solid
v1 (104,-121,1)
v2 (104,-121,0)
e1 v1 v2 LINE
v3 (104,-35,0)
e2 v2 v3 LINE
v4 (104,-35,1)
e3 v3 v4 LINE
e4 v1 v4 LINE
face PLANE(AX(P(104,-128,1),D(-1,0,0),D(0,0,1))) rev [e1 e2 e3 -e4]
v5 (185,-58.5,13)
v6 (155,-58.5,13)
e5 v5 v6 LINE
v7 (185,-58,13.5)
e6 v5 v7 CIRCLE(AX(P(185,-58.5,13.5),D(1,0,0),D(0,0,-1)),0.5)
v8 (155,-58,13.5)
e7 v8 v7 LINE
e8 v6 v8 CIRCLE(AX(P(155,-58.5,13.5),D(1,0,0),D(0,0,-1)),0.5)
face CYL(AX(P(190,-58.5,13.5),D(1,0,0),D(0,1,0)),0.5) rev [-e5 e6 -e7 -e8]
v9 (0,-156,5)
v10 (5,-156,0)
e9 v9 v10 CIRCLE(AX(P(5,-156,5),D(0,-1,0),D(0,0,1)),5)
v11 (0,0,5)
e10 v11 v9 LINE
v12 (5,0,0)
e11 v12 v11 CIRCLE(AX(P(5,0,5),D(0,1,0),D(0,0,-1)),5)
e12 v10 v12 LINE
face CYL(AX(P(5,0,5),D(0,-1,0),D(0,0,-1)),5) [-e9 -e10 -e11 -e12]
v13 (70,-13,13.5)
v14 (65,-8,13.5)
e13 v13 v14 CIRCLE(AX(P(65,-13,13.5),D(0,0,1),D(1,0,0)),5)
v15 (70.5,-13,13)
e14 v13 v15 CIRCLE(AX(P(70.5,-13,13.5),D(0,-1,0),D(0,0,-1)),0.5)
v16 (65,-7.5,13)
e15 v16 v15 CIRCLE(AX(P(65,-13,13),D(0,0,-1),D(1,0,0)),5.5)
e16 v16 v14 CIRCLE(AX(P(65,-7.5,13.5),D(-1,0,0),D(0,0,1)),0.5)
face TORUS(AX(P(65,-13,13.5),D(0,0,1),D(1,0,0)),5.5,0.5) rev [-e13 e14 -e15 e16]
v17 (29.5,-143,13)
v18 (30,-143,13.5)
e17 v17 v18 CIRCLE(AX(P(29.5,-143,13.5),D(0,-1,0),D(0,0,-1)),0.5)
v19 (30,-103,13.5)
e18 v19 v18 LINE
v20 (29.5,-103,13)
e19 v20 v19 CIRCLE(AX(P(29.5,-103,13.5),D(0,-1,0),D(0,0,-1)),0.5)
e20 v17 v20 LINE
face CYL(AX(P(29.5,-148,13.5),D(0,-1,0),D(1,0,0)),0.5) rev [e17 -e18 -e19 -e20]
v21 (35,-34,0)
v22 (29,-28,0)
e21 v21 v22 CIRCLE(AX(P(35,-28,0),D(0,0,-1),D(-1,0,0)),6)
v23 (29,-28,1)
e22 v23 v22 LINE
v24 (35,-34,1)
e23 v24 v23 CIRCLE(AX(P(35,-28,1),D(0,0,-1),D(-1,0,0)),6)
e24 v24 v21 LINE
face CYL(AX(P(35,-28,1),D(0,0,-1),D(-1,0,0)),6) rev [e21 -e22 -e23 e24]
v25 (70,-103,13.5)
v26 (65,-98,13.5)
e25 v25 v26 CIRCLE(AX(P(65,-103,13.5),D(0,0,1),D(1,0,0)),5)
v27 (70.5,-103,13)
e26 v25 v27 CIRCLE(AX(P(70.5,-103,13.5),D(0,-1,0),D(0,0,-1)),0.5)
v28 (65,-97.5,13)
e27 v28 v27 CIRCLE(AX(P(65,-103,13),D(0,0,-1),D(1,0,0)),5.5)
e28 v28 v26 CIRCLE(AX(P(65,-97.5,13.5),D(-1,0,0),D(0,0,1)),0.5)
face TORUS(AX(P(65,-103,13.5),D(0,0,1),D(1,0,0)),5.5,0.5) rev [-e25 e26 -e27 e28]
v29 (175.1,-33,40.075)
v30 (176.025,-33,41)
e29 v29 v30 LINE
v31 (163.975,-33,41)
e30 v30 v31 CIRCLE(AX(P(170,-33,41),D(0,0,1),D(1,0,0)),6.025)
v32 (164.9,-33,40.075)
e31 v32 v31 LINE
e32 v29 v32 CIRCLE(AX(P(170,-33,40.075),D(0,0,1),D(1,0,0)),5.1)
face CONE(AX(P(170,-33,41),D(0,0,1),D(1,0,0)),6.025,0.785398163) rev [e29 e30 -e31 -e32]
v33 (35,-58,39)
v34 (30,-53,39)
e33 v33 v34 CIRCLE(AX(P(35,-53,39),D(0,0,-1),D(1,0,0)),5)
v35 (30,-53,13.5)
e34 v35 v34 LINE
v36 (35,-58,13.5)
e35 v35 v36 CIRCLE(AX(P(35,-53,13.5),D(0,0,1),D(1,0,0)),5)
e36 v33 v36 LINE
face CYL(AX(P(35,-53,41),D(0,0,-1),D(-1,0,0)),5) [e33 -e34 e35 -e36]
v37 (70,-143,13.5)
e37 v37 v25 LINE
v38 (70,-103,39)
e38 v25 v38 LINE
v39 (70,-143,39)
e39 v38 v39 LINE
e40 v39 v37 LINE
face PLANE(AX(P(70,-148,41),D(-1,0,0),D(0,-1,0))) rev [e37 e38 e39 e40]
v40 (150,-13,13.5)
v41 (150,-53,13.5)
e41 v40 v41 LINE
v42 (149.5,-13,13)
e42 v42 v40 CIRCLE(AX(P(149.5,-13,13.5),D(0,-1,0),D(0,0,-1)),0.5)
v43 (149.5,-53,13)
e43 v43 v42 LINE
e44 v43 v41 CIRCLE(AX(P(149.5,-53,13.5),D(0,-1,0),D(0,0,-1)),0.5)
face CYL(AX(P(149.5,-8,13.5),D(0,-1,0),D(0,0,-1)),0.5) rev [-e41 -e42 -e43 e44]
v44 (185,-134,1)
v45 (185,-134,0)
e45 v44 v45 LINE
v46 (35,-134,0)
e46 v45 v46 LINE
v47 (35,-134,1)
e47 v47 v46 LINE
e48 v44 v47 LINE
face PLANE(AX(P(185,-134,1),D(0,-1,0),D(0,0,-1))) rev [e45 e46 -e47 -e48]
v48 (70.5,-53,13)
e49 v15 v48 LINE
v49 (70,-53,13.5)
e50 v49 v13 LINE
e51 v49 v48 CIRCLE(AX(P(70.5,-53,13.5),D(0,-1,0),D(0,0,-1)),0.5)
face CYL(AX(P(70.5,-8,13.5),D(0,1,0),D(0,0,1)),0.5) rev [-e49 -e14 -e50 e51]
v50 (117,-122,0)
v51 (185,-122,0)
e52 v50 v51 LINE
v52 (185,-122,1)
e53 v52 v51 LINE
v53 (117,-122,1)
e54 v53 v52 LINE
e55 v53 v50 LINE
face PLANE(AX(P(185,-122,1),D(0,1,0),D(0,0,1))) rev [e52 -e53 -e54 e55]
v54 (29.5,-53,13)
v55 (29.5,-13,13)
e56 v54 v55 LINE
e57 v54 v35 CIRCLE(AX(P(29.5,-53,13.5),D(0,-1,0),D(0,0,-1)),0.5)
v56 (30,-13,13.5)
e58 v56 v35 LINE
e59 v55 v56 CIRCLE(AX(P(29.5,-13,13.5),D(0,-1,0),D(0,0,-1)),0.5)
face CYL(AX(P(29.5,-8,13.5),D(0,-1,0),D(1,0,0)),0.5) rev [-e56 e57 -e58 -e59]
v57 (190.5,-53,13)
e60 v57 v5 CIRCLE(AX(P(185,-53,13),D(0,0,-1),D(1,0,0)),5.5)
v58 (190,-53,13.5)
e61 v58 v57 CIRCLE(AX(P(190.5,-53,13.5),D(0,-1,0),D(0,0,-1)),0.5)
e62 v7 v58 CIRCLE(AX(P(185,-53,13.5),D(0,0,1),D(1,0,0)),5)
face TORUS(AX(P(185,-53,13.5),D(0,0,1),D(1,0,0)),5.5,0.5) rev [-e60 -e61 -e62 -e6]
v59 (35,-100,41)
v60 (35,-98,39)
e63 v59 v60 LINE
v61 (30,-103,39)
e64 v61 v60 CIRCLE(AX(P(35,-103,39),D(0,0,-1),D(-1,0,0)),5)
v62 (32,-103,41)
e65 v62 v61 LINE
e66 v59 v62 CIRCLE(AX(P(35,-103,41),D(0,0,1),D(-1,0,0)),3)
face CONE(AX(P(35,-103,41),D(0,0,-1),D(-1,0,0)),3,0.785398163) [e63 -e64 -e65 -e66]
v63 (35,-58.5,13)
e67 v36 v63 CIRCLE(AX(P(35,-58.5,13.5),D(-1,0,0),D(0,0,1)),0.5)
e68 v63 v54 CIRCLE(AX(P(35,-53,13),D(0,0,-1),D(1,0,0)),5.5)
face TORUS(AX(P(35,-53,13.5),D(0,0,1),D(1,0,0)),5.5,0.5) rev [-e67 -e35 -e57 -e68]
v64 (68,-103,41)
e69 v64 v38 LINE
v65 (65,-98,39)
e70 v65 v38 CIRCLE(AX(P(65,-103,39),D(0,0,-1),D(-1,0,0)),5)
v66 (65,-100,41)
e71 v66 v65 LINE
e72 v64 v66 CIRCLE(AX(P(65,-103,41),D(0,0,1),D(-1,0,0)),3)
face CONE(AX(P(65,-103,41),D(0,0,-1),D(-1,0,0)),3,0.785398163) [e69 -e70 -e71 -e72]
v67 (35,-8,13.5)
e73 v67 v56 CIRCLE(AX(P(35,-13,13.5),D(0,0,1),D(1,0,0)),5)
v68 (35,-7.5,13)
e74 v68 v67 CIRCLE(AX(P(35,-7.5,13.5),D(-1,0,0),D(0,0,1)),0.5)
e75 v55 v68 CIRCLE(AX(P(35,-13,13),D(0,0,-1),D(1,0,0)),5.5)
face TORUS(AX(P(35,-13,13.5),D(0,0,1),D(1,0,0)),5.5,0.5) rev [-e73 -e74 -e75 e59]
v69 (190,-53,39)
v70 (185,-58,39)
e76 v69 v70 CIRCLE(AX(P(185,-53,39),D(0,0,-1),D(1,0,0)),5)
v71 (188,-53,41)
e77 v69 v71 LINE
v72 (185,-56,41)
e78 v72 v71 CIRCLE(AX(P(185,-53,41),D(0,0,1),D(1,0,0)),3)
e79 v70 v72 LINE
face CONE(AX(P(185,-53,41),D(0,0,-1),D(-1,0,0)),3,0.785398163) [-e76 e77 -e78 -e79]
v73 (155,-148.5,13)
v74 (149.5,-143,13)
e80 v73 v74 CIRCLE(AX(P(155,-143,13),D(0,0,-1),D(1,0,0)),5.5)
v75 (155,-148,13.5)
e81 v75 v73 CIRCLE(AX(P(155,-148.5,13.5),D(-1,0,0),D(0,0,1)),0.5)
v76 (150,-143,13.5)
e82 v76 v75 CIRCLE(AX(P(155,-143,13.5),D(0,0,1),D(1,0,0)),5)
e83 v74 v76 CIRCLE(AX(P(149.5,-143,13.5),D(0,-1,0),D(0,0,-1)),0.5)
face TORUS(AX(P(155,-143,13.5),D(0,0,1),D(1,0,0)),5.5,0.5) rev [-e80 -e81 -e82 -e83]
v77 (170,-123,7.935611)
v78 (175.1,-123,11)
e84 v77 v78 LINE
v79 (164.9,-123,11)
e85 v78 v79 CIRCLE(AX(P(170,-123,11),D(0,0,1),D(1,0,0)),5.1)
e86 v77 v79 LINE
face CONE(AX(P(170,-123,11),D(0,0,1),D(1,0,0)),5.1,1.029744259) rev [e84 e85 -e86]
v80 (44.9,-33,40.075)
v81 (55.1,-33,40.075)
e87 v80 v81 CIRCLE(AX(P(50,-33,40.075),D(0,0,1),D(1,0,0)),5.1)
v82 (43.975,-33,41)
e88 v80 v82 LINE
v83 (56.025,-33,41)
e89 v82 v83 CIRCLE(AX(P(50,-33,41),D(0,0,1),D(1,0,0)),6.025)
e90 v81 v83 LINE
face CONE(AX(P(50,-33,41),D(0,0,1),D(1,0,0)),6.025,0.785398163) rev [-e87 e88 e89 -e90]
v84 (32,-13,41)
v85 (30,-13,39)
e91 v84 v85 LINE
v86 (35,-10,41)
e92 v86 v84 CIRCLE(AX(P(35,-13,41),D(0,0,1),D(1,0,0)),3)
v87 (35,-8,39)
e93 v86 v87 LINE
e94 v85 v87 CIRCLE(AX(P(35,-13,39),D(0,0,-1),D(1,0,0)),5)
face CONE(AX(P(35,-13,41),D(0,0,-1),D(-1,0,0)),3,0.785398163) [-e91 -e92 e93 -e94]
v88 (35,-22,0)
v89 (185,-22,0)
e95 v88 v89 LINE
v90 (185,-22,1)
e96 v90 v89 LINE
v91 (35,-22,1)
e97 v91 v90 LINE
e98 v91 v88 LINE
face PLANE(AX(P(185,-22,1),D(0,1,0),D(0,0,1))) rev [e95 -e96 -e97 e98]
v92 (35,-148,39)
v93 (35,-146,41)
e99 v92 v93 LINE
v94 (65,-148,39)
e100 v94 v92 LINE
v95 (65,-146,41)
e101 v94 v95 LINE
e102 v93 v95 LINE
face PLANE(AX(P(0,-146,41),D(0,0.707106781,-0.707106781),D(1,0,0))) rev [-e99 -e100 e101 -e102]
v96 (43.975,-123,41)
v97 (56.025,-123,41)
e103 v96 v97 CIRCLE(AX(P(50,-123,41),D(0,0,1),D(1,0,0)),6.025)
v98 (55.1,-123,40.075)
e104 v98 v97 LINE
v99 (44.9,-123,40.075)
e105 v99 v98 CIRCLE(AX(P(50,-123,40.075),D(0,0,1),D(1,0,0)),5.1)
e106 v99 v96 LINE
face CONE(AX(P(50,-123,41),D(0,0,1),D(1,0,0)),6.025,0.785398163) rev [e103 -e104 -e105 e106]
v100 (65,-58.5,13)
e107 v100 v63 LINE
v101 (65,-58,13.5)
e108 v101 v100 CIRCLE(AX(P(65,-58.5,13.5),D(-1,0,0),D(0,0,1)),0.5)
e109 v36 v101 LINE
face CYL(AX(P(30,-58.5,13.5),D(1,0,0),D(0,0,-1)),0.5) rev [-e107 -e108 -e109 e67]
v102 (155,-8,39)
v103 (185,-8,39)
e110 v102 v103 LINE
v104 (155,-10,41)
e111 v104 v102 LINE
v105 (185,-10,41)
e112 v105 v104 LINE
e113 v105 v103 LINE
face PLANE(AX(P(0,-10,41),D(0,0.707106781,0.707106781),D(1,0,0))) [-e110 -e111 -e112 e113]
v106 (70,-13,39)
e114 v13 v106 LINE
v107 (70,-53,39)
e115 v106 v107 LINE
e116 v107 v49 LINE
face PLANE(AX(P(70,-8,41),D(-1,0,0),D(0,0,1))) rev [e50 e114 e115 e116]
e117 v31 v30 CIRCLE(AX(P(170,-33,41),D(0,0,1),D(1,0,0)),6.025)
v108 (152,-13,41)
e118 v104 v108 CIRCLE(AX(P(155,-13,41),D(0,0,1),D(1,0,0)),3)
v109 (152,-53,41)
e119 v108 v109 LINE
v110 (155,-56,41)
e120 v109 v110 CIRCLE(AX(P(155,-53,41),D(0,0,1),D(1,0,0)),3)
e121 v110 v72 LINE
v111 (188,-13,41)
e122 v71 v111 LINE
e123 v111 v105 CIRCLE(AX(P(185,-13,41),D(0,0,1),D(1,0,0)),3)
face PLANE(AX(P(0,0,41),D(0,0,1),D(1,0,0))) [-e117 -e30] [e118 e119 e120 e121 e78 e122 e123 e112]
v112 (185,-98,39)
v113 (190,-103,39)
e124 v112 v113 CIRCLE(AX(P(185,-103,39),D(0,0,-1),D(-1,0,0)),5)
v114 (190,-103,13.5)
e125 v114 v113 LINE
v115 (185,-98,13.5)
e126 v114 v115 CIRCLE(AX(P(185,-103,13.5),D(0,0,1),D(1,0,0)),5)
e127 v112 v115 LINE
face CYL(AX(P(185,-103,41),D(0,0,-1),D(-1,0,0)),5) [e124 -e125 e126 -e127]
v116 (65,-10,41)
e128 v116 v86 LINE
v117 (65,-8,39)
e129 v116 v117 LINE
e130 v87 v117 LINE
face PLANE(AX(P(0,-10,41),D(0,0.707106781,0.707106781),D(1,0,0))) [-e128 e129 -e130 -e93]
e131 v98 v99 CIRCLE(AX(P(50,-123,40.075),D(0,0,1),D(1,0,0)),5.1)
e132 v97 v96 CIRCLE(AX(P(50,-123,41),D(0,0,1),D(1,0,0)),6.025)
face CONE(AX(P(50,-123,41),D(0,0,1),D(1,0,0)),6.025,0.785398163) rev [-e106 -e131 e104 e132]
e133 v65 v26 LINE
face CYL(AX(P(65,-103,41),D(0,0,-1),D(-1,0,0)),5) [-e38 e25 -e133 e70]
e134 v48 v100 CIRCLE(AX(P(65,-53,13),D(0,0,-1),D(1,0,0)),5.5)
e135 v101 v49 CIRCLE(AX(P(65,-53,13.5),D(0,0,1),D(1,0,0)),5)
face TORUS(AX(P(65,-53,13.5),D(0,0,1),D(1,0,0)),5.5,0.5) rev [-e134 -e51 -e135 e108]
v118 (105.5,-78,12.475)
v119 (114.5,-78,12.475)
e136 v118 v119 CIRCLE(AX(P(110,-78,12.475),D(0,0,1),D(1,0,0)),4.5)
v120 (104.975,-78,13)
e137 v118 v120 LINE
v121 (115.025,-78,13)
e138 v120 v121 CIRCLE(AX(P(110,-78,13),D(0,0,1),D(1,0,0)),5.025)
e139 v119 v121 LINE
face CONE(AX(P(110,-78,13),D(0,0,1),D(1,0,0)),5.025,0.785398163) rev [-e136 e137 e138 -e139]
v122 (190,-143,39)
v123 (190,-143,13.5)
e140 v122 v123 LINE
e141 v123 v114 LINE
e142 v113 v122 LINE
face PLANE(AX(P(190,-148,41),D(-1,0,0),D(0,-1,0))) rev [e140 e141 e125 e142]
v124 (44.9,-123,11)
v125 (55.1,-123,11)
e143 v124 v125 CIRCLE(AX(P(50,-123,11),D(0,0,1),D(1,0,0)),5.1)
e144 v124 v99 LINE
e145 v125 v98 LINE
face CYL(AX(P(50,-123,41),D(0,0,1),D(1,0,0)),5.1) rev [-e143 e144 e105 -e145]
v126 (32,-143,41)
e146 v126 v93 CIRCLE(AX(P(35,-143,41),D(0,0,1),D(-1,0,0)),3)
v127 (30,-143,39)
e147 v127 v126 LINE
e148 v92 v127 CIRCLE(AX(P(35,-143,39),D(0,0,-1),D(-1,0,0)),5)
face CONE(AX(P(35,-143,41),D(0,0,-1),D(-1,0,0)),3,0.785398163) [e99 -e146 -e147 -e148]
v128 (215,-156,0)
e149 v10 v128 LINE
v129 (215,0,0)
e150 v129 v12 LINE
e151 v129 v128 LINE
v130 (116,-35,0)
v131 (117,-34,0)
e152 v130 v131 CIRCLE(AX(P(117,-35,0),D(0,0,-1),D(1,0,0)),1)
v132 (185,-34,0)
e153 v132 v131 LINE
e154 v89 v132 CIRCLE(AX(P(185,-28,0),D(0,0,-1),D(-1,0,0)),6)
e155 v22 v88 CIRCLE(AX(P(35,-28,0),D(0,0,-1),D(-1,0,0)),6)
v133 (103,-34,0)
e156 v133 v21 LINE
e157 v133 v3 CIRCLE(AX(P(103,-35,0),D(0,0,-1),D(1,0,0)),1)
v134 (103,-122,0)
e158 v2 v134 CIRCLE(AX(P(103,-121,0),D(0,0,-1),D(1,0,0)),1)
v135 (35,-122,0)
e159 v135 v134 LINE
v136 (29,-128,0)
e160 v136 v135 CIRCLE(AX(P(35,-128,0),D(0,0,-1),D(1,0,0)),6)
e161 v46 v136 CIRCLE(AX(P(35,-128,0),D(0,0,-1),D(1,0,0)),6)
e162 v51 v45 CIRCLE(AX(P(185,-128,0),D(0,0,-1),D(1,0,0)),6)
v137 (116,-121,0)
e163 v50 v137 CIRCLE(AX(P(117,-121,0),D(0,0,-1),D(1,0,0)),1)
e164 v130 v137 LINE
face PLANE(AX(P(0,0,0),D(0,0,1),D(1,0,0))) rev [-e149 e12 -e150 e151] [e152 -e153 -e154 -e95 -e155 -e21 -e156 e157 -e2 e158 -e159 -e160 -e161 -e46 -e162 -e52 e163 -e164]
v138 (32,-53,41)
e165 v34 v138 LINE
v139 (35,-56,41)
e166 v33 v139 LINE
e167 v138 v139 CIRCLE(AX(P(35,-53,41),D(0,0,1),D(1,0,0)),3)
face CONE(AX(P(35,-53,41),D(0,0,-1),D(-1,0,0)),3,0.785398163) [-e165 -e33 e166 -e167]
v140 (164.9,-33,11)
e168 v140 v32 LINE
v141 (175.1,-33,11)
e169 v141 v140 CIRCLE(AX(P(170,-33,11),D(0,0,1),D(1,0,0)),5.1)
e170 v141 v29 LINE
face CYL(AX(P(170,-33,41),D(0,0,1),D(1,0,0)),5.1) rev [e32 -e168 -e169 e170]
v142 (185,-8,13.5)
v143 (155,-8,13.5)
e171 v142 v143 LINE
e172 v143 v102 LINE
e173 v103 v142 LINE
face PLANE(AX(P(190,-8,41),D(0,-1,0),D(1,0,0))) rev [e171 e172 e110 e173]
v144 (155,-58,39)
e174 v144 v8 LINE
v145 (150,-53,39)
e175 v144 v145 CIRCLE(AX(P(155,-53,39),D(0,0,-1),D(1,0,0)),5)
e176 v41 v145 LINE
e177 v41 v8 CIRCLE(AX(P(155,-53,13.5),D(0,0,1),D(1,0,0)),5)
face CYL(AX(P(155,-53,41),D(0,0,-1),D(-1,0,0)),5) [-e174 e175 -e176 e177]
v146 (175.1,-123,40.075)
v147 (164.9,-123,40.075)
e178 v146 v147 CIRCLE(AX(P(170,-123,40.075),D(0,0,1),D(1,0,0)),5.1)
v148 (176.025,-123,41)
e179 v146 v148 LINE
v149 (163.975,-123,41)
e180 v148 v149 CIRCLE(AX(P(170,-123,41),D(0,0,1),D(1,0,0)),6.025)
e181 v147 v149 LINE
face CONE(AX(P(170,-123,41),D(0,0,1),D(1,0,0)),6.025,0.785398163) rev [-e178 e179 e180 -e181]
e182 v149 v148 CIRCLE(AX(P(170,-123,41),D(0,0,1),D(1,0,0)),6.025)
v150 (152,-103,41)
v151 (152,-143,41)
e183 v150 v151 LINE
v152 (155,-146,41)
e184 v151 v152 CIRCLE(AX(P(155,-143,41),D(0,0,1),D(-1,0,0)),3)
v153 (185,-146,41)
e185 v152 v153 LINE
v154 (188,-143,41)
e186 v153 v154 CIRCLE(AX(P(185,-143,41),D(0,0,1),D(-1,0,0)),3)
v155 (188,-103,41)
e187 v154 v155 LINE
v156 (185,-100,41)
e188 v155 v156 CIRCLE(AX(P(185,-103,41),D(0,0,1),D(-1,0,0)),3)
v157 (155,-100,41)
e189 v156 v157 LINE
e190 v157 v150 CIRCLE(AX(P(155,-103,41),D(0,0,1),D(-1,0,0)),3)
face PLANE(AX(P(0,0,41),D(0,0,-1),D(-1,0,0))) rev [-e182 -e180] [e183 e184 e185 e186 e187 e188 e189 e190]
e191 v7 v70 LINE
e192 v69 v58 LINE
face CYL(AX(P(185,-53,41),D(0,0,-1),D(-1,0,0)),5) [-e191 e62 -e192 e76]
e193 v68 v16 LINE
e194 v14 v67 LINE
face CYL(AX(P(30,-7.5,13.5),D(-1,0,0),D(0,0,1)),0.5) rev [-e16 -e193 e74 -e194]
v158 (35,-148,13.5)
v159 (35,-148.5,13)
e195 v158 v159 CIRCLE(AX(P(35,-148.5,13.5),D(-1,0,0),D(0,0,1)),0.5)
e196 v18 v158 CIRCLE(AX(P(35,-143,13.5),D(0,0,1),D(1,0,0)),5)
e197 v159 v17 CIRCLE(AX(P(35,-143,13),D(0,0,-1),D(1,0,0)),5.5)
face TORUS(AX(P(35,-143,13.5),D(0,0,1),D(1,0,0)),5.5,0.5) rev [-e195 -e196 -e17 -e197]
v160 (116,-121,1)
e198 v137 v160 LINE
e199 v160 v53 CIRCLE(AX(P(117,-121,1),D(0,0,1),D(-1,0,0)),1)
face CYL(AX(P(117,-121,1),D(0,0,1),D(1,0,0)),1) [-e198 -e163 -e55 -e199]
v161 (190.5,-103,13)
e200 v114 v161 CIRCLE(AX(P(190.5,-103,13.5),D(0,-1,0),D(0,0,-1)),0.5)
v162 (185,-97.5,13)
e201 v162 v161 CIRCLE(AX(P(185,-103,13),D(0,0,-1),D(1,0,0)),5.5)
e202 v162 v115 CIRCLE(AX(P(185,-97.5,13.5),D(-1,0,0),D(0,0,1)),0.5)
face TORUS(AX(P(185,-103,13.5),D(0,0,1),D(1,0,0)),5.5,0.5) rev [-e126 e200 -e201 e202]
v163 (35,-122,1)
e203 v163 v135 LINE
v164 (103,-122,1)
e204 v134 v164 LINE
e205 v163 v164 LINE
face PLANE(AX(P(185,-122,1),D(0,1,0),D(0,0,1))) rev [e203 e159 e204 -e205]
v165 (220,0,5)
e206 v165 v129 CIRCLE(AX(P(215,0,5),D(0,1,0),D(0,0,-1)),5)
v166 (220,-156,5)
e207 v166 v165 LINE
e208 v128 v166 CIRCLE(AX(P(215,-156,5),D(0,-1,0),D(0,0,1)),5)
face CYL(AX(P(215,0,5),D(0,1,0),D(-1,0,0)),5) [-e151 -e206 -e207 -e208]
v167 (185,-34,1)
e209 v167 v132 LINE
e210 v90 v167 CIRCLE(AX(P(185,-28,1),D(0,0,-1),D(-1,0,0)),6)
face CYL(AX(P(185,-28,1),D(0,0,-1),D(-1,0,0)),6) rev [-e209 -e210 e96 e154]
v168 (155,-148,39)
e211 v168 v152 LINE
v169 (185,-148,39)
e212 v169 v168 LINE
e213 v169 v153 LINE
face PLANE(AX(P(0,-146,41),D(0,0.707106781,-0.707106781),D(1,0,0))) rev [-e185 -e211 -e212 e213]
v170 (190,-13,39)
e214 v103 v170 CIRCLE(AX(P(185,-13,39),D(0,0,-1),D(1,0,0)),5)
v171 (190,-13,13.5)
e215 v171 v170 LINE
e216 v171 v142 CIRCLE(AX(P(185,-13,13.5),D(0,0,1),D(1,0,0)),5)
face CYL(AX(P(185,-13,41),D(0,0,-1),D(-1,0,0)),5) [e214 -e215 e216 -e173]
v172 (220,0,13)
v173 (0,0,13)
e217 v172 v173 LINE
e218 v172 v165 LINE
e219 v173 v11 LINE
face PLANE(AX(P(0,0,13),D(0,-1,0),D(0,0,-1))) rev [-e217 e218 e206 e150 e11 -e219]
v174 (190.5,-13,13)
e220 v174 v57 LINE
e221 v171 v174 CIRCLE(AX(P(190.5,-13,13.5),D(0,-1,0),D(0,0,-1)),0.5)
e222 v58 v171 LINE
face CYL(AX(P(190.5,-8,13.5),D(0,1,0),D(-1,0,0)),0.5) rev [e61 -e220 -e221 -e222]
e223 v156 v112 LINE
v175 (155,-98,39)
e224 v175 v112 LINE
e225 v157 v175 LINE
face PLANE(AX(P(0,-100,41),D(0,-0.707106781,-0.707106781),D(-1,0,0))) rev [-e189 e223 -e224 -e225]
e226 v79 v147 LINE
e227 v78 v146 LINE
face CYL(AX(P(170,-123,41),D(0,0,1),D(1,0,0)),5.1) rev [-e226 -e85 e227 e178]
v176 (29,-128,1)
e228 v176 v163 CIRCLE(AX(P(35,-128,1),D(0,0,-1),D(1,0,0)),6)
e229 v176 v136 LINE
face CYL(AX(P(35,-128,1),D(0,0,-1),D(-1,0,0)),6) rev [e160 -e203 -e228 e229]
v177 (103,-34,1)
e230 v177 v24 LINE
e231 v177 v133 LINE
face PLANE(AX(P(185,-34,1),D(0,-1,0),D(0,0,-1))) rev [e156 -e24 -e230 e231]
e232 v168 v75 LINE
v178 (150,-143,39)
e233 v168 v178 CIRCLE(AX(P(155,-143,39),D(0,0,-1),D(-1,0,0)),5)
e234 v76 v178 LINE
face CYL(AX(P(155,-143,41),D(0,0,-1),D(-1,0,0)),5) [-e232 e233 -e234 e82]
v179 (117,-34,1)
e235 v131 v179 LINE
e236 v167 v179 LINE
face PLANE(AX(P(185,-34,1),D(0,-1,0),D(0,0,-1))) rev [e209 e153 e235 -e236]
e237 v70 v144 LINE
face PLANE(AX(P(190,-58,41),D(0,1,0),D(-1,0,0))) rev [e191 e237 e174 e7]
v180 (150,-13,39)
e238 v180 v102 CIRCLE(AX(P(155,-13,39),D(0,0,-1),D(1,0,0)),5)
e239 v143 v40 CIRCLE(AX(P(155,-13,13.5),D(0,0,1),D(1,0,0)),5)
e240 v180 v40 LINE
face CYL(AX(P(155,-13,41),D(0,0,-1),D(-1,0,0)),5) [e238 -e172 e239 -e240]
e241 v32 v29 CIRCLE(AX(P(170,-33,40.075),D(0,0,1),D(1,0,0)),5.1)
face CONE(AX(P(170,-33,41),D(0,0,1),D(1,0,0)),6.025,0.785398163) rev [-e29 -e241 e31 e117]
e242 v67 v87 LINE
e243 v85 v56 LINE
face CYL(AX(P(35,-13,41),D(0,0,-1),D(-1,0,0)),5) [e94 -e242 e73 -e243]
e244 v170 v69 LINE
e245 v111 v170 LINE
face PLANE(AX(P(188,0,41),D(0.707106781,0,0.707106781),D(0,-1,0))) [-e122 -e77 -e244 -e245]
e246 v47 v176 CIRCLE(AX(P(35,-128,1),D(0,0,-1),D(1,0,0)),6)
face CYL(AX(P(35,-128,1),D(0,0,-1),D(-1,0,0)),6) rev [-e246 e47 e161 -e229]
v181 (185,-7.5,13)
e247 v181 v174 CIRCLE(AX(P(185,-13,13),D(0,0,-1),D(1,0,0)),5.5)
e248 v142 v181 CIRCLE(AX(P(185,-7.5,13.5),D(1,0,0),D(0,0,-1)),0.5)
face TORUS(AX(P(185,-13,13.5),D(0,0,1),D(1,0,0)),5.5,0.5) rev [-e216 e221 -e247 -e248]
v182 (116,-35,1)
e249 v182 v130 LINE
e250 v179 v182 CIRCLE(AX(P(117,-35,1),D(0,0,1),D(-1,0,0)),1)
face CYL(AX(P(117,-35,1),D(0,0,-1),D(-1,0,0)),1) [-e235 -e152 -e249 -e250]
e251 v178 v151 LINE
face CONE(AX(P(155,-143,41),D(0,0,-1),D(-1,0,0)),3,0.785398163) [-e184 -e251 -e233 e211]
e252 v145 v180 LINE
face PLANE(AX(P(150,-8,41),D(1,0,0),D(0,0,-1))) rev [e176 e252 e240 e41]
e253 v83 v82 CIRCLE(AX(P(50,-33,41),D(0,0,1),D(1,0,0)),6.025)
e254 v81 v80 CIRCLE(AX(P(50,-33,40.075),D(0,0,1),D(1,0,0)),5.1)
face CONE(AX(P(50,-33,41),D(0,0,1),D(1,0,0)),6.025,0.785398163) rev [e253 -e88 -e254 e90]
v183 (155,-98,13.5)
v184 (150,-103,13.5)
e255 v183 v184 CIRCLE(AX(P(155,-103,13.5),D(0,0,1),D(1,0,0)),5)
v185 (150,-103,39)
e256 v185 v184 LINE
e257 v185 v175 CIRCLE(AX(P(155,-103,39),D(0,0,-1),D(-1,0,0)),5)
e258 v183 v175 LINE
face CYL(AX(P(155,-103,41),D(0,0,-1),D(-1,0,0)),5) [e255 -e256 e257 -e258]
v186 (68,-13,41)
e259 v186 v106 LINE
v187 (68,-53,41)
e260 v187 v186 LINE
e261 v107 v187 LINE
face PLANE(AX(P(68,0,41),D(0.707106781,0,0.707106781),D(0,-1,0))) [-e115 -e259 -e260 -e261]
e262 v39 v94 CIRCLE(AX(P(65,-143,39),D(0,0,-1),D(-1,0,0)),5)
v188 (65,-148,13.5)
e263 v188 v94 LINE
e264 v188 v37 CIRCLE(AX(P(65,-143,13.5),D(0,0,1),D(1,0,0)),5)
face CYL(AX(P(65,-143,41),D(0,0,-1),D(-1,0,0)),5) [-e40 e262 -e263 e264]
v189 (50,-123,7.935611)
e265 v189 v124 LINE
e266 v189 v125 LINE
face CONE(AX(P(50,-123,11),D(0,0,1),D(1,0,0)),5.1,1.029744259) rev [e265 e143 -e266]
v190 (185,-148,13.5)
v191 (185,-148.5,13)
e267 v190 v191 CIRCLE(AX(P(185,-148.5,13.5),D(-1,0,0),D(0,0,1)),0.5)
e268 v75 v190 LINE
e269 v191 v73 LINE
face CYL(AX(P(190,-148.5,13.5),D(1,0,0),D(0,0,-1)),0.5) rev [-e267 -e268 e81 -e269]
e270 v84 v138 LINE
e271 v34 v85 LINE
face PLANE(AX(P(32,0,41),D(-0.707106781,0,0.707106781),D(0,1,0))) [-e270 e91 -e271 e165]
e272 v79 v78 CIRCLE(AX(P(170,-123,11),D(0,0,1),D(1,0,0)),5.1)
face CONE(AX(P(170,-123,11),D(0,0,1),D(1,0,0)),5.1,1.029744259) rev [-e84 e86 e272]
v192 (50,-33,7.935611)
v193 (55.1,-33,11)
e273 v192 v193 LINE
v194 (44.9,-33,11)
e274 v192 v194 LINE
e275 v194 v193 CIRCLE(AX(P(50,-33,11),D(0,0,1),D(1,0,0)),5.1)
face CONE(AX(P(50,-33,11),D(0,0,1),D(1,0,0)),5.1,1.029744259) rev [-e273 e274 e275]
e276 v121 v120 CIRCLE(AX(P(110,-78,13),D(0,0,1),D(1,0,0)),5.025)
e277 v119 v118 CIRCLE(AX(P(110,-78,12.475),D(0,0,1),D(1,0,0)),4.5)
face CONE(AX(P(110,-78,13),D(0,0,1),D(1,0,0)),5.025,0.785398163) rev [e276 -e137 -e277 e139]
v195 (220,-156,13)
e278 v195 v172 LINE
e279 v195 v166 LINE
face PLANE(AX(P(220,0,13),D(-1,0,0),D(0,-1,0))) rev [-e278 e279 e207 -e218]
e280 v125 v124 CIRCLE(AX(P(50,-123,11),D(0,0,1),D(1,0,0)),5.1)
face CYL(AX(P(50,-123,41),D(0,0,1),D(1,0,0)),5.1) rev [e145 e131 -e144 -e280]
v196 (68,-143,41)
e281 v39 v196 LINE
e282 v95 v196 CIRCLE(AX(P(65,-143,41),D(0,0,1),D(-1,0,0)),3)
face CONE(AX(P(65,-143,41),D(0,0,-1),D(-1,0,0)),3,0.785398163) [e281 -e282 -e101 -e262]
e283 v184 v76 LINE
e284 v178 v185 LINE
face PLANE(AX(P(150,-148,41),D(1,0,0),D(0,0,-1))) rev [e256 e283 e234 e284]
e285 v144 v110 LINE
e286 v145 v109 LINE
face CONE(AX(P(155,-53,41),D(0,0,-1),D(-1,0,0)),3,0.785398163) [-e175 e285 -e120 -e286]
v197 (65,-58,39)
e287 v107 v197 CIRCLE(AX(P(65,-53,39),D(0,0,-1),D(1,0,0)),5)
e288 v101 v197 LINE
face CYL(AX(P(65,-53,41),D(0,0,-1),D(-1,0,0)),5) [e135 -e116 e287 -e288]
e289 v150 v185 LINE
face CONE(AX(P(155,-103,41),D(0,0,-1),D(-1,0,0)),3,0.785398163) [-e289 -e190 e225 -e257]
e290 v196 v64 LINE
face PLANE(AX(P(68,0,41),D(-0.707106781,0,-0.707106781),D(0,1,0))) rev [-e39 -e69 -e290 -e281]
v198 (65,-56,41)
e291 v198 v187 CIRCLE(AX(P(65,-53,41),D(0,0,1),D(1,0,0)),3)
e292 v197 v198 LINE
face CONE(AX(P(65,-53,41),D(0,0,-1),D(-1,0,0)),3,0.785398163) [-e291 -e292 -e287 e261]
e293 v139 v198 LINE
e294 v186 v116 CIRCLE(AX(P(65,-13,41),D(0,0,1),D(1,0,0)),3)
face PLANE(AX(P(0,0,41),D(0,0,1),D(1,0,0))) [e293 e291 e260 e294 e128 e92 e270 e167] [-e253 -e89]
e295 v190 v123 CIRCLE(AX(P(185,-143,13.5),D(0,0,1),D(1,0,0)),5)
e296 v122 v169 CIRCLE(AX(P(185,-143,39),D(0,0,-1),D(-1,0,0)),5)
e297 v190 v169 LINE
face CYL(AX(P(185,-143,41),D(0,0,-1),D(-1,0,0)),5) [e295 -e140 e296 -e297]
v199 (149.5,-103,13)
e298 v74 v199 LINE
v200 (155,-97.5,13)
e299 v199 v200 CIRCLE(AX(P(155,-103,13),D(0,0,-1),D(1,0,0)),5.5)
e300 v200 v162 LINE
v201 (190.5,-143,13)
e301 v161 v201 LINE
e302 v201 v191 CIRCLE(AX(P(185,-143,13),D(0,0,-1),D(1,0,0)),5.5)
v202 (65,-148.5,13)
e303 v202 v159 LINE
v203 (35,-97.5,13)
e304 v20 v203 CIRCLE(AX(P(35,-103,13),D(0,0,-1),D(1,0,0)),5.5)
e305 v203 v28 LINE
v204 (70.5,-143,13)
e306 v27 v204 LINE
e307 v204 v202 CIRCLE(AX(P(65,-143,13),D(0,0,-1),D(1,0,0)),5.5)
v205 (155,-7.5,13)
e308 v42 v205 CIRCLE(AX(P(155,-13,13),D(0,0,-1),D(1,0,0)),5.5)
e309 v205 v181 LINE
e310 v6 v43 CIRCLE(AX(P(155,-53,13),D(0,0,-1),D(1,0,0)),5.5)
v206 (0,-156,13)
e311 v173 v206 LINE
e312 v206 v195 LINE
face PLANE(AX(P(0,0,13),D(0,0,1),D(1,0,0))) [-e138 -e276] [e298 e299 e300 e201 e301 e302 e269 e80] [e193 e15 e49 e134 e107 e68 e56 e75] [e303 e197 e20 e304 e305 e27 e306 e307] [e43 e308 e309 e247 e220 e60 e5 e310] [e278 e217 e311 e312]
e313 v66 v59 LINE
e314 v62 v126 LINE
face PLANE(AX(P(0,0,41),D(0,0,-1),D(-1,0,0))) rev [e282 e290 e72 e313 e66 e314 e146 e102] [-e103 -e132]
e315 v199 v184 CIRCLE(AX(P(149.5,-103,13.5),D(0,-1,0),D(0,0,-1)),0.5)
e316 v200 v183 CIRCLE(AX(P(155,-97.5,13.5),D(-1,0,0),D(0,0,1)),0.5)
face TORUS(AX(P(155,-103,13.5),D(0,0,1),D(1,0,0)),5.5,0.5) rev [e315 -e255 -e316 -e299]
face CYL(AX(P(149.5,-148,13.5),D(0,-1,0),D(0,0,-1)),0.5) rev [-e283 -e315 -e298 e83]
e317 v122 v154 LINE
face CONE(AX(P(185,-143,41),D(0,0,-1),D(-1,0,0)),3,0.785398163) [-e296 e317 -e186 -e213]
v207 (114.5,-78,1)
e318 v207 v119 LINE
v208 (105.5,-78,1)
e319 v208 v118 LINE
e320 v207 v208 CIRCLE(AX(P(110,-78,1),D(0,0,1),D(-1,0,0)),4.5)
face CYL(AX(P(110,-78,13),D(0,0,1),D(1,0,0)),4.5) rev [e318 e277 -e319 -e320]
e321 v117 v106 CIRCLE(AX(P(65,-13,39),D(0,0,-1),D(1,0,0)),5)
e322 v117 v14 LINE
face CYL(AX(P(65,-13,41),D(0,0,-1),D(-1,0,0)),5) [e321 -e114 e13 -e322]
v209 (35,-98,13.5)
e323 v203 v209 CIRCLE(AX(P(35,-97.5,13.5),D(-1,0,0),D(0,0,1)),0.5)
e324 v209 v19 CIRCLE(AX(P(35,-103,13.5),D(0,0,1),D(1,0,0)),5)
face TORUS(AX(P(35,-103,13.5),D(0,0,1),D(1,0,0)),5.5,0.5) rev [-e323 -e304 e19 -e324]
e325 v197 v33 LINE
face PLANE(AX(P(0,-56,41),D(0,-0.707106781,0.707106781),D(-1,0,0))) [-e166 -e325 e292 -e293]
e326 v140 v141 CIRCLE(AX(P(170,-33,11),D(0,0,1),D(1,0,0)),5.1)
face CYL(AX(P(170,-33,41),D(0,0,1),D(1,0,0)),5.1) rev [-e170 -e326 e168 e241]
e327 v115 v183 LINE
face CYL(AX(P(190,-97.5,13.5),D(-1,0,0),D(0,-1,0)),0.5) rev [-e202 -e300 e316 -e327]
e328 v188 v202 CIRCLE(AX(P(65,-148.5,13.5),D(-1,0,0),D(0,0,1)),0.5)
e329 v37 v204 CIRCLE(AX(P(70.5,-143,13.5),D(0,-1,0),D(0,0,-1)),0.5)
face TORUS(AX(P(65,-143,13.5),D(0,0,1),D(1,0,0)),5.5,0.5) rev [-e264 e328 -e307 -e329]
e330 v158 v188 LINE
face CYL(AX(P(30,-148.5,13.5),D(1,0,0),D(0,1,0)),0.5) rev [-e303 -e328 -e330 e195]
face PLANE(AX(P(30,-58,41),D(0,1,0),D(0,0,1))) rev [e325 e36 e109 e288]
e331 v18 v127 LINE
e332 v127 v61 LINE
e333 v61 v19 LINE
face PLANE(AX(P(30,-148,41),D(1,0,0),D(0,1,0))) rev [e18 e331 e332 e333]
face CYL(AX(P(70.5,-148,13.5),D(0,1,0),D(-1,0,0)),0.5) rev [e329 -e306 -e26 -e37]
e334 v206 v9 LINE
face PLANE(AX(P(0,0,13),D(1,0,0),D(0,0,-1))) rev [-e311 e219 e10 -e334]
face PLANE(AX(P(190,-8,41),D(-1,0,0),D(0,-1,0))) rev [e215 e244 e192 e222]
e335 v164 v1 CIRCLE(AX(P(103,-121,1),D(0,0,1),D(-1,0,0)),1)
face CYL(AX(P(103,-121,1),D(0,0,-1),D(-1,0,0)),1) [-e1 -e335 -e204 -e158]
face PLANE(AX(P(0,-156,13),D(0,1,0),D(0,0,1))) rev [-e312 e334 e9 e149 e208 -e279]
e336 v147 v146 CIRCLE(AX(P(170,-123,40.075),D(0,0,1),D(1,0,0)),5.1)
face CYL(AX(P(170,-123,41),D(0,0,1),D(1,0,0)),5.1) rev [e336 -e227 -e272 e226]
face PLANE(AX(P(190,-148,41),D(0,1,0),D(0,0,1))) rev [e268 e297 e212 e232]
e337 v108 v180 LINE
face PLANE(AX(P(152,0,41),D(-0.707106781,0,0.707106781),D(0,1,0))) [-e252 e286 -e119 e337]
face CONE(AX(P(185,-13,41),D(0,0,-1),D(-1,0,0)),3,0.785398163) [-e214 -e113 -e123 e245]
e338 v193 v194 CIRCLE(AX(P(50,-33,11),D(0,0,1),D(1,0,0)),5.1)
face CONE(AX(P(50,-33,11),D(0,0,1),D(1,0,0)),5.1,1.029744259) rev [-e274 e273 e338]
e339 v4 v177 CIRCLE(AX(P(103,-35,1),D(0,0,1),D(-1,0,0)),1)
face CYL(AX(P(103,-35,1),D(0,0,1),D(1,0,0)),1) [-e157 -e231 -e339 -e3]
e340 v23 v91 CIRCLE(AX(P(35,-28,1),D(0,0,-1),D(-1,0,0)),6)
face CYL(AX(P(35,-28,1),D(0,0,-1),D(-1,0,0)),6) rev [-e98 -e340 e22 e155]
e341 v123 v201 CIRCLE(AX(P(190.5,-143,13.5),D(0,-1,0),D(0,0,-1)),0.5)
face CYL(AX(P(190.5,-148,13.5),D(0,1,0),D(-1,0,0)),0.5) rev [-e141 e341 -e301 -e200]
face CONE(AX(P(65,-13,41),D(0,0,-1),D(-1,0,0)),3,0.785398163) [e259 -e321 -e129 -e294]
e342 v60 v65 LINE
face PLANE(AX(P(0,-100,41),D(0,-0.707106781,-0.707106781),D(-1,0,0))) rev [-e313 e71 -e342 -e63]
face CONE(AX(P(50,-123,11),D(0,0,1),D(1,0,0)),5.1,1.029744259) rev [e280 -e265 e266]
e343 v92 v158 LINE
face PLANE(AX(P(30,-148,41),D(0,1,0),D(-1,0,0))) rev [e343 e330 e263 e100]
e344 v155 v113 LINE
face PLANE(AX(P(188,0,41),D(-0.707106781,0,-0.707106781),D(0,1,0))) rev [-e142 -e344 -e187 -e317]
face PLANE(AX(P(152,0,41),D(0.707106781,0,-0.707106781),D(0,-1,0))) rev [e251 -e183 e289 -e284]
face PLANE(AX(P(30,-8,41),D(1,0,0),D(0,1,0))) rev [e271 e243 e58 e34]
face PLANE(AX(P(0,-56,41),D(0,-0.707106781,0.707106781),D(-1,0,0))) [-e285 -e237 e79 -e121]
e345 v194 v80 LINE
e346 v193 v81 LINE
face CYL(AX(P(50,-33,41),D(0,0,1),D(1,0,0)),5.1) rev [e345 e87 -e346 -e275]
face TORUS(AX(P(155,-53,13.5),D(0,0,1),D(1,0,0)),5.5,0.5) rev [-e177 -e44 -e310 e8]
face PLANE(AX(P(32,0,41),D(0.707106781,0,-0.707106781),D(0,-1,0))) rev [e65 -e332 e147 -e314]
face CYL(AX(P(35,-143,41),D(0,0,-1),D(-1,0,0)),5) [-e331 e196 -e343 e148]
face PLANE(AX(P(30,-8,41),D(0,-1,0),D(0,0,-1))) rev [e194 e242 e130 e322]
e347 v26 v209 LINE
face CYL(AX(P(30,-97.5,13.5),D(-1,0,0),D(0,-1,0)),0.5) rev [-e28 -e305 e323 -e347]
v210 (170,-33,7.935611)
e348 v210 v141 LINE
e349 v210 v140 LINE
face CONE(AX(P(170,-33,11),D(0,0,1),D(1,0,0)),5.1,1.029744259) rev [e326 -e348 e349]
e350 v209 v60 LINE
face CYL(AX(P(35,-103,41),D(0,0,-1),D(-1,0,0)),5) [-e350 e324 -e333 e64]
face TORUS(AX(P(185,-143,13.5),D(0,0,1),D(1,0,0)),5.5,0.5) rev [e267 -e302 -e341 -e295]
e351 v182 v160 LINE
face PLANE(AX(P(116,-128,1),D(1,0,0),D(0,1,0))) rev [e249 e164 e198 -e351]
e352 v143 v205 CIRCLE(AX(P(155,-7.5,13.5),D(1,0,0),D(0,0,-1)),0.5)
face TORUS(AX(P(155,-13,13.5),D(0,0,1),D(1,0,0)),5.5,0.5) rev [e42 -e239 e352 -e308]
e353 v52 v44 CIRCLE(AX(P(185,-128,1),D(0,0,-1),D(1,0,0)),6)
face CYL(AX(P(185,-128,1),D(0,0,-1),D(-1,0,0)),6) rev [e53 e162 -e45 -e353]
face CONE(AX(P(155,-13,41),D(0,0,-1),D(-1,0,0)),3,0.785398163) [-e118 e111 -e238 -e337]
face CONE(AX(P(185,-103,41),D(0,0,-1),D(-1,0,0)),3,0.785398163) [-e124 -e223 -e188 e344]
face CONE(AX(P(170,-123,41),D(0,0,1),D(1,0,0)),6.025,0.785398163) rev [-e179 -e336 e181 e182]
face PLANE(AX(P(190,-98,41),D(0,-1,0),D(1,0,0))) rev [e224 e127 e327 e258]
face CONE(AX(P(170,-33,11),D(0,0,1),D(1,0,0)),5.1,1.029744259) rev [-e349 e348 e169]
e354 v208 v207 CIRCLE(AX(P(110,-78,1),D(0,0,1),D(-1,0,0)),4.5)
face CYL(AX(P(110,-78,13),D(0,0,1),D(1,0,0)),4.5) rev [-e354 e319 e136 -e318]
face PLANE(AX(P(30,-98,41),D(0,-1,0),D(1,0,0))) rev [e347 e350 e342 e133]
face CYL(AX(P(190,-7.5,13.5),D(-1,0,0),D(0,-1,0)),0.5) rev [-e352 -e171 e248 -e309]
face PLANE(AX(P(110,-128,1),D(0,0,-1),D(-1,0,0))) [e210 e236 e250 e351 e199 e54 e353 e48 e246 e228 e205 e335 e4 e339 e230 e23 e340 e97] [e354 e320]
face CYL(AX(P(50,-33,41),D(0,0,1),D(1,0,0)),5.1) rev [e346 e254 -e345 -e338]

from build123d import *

# Parameters (mm, degrees)
SKETCH_1_W                    = 220
SKETCH_1_H                    = 156
EXTRUDE_1_DEPTH               = 13
SKETCH_2_W                    = 40
SKETCH_2_H                    = 50
EXTRUDE_2_DEPTH               = 28
FILLET_1_R                    = 5
HOLE_WIZARD_M12_1_D           = 10.2
HOLE_WIZARD_M12_1_DEPTH       = 30
HOLE_WIZARD_M12_1_CSINK_D     = 12.05
HOLE_WIZARD_M12_1_CSINK_ANGLE = 90
HOLE_WIZARD_M12_1_TIP         = 3.064389157
M10X1_0_1_D                   = 9
M10X1_0_1_DEPTH               = 25
M10X1_0_1_CSINK_D             = 10.05
M10X1_0_1_CSINK_ANGLE         = 90
M10X1_0_1_TIP                 = 2.703872786
FILLET_2_R                    = 5
CHAMFER_1_SIZE                = 2
CUT_EXTRUDE_1_DEPTH           = 1
CUT_EXTRUDE_2_DEPTH           = 1
FILLET_3_R                    = 0.5
FILLET_4_R                    = 1


with BuildPart() as part:
    # 草图1 → 凸台-拉伸1 (new body)
    with BuildSketch(Plane.XY):
        with Locations((110, -78)):
            Rectangle(SKETCH_1_W, SKETCH_1_H)
    extrude(amount=EXTRUDE_1_DEPTH)

    # 草图2 → 凸台-拉伸2 (add)
    with BuildSketch(Plane.XY.offset(13)):
        with Locations((50, -33)):
            Rectangle(SKETCH_2_W, SKETCH_2_H)
        with Locations((170, -33)):
            Rectangle(SKETCH_2_W, SKETCH_2_H)
        with Locations((170, -123)):
            Rectangle(SKETCH_2_W, SKETCH_2_H)
        with Locations((50, -123)):
            Rectangle(SKETCH_2_W, SKETCH_2_H)
    extrude(amount=EXTRUDE_2_DEPTH)

    # 圆角1
    fillet_1_edges = [part.edges().sort_by_distance(p)[0] for p in [
        (220, -78, 0),
        (0, -78, 0),
    ]]
    fillet(fillet_1_edges, radius=FILLET_1_R)

    # M12 螺纹孔1
    with Locations(Plane(origin=(50, -33, 41), x_dir=(1, 0, 0), z_dir=(0, 0, 1))):
        with Locations((0, 0), (120, 0), (120, -90), (0, -90)):
            CounterSinkHole(HOLE_WIZARD_M12_1_D / 2, HOLE_WIZARD_M12_1_CSINK_D / 2, depth=HOLE_WIZARD_M12_1_DEPTH, counter_sink_angle=HOLE_WIZARD_M12_1_CSINK_ANGLE)
            with Locations((0, 0, -(HOLE_WIZARD_M12_1_DEPTH + HOLE_WIZARD_M12_1_TIP / 2))):  # 118° drill point
                Cone(0, HOLE_WIZARD_M12_1_D / 2, HOLE_WIZARD_M12_1_TIP, mode=Mode.SUBTRACT)

    # M10x1.0 螺纹孔1
    with Locations(Plane(origin=(110, -78, 13), x_dir=(1, 0, 0), z_dir=(0, 0, 1))):
        with Locations((0, 0)):
            CounterSinkHole(M10X1_0_1_D / 2, M10X1_0_1_CSINK_D / 2, depth=M10X1_0_1_DEPTH, counter_sink_angle=M10X1_0_1_CSINK_ANGLE)
            with Locations((0, 0, -(M10X1_0_1_DEPTH + M10X1_0_1_TIP / 2))):  # 118° drill point
                Cone(0, M10X1_0_1_D / 2, M10X1_0_1_TIP, mode=Mode.SUBTRACT)

    # 圆角2
    fillet_2_edges = [part.edges().sort_by_distance(p)[0] for p in [
        (70, -58, 27),
        (70, -8, 27),
        (30, -8, 27),
        (30, -58, 27),
        (190, -8, 27),
        (150, -8, 27),
        (150, -58, 27),
        (190, -58, 27),
        (150, -148, 27),
        (190, -148, 27),
        (190, -98, 27),
        (150, -98, 27),
        (30, -98, 27),
        (30, -148, 27),
        (70, -148, 27),
        (70, -98, 27),
    ]]
    fillet(fillet_2_edges, radius=FILLET_2_R)

    # 倒角1
    chamfer_1_edges = [part.edges().sort_by_distance(p)[0] for p in [
        (50, -98, 41),
        (70, -123, 41),
        (30, -123, 41),
        (50, -148, 41),
        (68.535533906, -146.535533906, 41),
        (31.464466094, -146.535533906, 41),
        (31.464466094, -99.464466094, 41),
        (68.535533906, -99.464466094, 41),
        (170, -148, 41),
        (150, -123, 41),
        (190, -123, 41),
        (170, -98, 41),
        (151.464466094, -99.464466094, 41),
        (188.535533906, -99.464466094, 41),
        (188.535533906, -146.535533906, 41),
        (151.464466094, -146.535533906, 41),
        (150, -33, 41),
        (170, -8, 41),
        (170, -58, 41),
        (190, -33, 41),
        (151.464466094, -56.535533906, 41),
        (188.535533906, -56.535533906, 41),
        (188.535533906, -9.464466094, 41),
        (151.464466094, -9.464466094, 41),
        (70, -33, 41),
        (50, -58, 41),
        (50, -8, 41),
        (30, -33, 41),
        (31.464466094, -9.464466094, 41),
        (68.535533906, -9.464466094, 41),
        (31.464466094, -56.535533906, 41),
        (68.535533906, -56.535533906, 41),
    ]]
    chamfer(chamfer_1_edges, length=CHAMFER_1_SIZE)

    # 草图12 → 切除-拉伸1 (cut)
    with BuildSketch(Plane(origin=(0, 0, 0), x_dir=(-1, 0, 0), z_dir=(0, 0, -1))):
        with BuildLine():
            Line((-116, -128), (-116, -28))
            ThreePointArc((-116, -28), (-110, -22), (-104, -28))
            Line((-104, -28), (-104, -128))
            ThreePointArc((-104, -128), (-110, -134), (-116, -128))
        make_face()
    extrude(amount=-CUT_EXTRUDE_1_DEPTH, mode=Mode.SUBTRACT)

    # 草图13 → 切除-拉伸2 (cut)
    with BuildSketch(Plane(origin=(0, 0, 0), x_dir=(-1, 0, 0), z_dir=(0, 0, -1))):
        with BuildLine():
            Line((-185, -22), (-35, -22))
            ThreePointArc((-35, -22), (-29, -28), (-35, -34))
            Line((-35, -34), (-185, -34))
            ThreePointArc((-185, -34), (-191, -28), (-185, -22))
        make_face()
        with BuildLine():
            Line((-185, -134), (-35, -134))
            ThreePointArc((-35, -134), (-29, -128), (-35, -122))
            Line((-35, -122), (-185, -122))
            ThreePointArc((-185, -122), (-191, -128), (-185, -134))
        make_face()
    extrude(amount=-CUT_EXTRUDE_2_DEPTH, mode=Mode.SUBTRACT)

    # 圆角3
    fillet_3_edges = [part.edges().sort_by_distance(p)[0] for p in [
        (50, -98, 13),
        (70, -123, 13),
        (30, -123, 13),
        (50, -148, 13),
        (170, -148, 13),
        (150, -123, 13),
        (190, -123, 13),
        (170, -98, 13),
        (150, -33, 13),
        (170, -8, 13),
        (190, -33, 13),
        (170, -58, 13),
        (70, -33, 13),
        (50, -58, 13),
        (30, -33, 13),
        (50, -8, 13),
        (68.535533906, -99.464466094, 13),
        (31.464466094, -99.464466094, 13),
        (31.464466094, -146.535533906, 13),
        (68.535533906, -146.535533906, 13),
        (151.464466094, -146.535533906, 13),
        (188.535533906, -146.535533906, 13),
        (188.535533906, -99.464466094, 13),
        (151.464466094, -99.464466094, 13),
        (151.464466094, -9.464466094, 13),
        (188.535533906, -9.464466094, 13),
        (188.535533906, -56.535533906, 13),
        (151.464466094, -56.535533906, 13),
        (68.535533906, -56.535533906, 13),
        (31.464466094, -56.535533906, 13),
        (68.535533906, -9.464466094, 13),
        (31.464466094, -9.464466094, 13),
    ]]
    fillet(fillet_3_edges, radius=FILLET_3_R)

    # 圆角4
    fillet_4_edges = [part.edges().sort_by_distance(p)[0] for p in [
        (104, -122, 0.5),
        (104, -34, 0.5),
        (116, -34, 0.5),
        (116, -122, 0.5),
    ]]
    fillet(fillet_4_edges, radius=FILLET_4_R)


solid = part.part
